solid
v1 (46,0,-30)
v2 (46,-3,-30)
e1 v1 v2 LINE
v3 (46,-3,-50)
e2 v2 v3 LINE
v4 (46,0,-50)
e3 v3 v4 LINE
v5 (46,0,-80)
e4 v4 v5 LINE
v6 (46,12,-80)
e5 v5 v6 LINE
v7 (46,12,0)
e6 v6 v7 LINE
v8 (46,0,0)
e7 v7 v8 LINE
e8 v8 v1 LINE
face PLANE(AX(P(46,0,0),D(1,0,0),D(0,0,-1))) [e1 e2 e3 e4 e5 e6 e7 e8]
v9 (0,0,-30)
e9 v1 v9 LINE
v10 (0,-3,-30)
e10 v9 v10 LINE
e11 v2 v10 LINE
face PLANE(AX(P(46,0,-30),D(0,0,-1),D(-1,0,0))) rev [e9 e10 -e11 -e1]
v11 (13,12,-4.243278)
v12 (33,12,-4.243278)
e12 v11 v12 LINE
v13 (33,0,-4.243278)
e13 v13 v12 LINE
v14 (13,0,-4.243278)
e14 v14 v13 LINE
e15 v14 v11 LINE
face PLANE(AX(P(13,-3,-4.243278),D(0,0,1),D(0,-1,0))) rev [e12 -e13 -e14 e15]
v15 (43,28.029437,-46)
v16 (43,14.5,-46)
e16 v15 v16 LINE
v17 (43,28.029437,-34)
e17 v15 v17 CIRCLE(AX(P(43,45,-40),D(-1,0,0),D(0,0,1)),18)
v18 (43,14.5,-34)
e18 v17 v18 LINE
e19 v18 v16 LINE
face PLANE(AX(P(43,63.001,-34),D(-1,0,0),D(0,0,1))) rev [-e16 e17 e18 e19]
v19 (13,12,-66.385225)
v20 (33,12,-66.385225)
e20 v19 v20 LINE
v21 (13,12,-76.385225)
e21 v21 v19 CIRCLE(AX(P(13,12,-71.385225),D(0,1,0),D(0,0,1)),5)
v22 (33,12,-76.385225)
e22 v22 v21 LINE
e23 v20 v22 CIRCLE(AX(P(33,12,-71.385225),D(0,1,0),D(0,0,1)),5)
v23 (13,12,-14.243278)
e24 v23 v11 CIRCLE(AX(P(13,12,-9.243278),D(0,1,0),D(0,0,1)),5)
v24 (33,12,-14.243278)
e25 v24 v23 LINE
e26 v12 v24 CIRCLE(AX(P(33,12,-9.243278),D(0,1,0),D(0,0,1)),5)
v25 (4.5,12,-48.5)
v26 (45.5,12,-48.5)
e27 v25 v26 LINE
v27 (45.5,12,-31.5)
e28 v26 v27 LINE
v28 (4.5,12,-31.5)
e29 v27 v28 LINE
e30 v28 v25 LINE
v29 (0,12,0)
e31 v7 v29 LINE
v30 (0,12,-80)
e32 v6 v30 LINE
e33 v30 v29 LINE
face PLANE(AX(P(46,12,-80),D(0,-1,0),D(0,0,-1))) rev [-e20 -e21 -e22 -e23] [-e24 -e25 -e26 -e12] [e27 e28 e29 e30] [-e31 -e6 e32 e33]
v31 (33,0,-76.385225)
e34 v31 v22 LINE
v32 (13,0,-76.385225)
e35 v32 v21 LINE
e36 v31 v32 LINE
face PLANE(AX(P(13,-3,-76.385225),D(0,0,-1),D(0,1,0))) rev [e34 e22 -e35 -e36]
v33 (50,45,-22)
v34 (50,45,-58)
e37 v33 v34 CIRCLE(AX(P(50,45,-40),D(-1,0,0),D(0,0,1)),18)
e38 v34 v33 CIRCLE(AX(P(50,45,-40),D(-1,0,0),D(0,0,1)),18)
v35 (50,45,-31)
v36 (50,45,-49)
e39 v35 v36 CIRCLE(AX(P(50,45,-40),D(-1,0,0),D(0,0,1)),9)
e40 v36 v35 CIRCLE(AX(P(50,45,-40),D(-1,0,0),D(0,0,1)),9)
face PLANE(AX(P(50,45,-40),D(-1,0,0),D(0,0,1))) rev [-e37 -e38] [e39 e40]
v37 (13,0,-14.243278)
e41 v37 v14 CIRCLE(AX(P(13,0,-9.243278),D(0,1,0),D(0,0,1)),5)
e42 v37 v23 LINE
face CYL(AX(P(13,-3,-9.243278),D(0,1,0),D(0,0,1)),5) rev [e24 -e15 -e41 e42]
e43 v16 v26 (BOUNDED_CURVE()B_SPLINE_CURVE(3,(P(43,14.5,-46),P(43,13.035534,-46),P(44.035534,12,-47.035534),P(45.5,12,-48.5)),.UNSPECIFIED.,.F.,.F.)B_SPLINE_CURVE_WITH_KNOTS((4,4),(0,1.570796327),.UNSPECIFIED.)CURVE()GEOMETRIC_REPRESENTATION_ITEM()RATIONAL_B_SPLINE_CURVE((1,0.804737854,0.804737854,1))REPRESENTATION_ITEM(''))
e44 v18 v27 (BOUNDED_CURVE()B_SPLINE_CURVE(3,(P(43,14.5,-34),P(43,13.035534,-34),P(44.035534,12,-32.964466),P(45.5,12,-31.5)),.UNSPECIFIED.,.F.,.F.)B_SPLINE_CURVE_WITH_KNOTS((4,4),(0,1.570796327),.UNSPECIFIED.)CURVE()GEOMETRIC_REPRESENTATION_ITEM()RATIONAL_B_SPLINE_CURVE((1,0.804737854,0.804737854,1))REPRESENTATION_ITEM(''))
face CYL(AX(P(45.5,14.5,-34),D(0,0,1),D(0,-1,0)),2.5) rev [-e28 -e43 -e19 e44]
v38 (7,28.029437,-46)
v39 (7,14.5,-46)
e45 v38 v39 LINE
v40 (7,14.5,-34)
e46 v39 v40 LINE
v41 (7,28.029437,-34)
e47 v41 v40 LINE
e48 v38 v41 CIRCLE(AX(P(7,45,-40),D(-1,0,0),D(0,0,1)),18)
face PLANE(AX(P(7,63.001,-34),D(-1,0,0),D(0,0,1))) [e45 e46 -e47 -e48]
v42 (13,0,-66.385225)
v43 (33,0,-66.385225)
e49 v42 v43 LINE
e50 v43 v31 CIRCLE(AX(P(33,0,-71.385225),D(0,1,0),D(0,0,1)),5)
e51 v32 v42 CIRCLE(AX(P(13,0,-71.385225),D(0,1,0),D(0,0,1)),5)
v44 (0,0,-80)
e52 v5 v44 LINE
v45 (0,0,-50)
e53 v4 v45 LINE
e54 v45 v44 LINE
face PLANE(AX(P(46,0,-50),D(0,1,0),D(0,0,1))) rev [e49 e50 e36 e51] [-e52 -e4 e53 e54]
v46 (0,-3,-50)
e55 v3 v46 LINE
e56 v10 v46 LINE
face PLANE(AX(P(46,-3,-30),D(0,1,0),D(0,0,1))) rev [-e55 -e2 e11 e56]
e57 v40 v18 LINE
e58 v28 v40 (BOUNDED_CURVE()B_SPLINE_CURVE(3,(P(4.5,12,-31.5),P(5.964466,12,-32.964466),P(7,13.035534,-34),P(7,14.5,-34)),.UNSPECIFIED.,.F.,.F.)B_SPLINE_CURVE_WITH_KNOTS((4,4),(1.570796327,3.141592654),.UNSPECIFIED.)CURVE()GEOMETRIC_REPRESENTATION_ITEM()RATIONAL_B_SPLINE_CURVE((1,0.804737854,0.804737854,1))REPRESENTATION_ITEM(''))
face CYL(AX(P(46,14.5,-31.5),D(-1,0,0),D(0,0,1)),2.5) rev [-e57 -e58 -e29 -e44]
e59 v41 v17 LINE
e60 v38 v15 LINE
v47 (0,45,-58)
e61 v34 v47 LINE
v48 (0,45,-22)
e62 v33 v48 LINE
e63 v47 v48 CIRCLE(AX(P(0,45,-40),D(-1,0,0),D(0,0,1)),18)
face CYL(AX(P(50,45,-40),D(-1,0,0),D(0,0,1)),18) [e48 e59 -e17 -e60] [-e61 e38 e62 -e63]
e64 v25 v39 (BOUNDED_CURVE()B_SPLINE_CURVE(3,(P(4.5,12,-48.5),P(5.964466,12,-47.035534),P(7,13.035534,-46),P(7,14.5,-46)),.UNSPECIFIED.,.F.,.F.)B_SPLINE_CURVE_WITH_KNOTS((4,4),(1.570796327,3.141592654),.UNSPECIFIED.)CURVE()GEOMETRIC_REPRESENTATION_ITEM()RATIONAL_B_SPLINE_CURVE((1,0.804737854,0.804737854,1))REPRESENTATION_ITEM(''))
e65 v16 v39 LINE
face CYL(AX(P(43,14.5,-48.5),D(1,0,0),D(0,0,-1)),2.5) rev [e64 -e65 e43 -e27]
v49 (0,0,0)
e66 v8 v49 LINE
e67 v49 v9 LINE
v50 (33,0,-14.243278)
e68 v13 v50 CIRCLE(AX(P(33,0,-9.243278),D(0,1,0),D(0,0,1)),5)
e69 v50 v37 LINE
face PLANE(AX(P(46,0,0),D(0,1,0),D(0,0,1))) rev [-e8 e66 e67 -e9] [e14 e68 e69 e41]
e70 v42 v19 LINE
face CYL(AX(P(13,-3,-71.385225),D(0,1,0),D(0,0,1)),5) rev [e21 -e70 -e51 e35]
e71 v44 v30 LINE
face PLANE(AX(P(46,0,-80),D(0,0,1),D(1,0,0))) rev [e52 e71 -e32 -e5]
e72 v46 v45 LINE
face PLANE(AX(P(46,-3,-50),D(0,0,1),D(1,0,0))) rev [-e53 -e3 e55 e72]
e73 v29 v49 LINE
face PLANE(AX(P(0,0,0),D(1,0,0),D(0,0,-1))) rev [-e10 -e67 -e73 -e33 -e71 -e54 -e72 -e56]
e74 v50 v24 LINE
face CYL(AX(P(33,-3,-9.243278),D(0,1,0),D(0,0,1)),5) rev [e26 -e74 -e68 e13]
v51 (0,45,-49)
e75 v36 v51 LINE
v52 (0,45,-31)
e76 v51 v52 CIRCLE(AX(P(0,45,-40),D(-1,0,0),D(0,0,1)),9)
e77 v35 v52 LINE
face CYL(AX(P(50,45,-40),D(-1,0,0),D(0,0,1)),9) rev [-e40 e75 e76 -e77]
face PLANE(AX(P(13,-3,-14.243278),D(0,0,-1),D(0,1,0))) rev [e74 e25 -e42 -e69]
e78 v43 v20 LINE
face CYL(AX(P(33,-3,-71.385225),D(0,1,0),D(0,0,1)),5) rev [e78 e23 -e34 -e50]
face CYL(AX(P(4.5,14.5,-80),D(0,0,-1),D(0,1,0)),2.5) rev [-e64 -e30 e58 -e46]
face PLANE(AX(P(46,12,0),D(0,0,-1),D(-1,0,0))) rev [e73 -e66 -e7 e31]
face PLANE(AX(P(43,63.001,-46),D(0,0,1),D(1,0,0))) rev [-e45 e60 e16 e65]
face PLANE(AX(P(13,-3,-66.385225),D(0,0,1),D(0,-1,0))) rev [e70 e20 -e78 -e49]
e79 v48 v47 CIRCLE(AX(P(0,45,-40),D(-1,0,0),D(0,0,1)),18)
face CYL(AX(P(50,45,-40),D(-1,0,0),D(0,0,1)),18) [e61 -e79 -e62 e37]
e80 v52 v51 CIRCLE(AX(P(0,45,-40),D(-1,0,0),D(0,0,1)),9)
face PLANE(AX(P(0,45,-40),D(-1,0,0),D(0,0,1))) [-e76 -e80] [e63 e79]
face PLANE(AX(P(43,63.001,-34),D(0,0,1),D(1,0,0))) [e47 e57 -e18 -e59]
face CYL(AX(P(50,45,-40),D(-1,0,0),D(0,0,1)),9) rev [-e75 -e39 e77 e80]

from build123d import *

# Parameters (mm, degrees)
BASE_PLATE_DEPTH             = 46
HUB_PROFILE_36_18_R          = 18
HUB_PROFILE_36_18_R_2        = 9
BEARING_HUB_36_BORE_18_DEPTH = 50
HUB_SUPPORT_WEB_REACH        = 109.243
HUB_SUPPORT_WEB_END_RADIUS   = 18
HUB_SUPPORT_PROFILE_W        = 36
HUB_SUPPORT_PROFILE_H        = 12
MOUNTING_SLOTS_2X_DEPTH      = 108.24271537
EDGE_FILLETS_R2_5_R          = 2.5


with BuildPart() as part:
    # Base Plate Profile → Base Plate (new body)
    with BuildSketch(Plane(origin=(0, 0, 0), x_dir=(0, 0, -1), z_dir=(1, 0, 0))):
        Polygon((0, 0), (30, 0), (30, -3), (50, -3), (50, 0), (80, 0), (80, 12), (0, 12), align=None)
    extrude(amount=BASE_PLATE_DEPTH)



with BuildPart() as body_2:
    # Hub Profile Ø36-Ø18 → Bearing Hub Ø36 Bore Ø18 (new body)
    with BuildSketch(Plane.ZY):
        with Locations((-40, 45)):
            Circle(HUB_PROFILE_36_18_R)
        with Locations((-40, 45)):
            Circle(HUB_PROFILE_36_18_R_2, mode=Mode.SUBTRACT)
    extrude(amount=-BEARING_HUB_36_BORE_18_DEPTH)


with BuildPart() as part_1:
    add(part.part)

    add(body_2.part)  # Hub Support Web merges body 2
    # Hub Support Web: up to this cylinder (the profile starts outside it)
    hub_support_web_end = Plane(origin=(25, 45, -40), z_dir=(-1, 0, 0)) * Cylinder(HUB_SUPPORT_WEB_END_RADIUS, 255.486, mode=Mode.PRIVATE)
    # Hub Support Profile → Hub Support Web (add, up to the surface)
    with BuildSketch(Plane(origin=(0, 12, 0), x_dir=(1, 0, 0), z_dir=(0, 1, 0)), mode=Mode.PRIVATE) as hub_support_web_sk1:
        with Locations((25, 40)):
            Rectangle(HUB_SUPPORT_PROFILE_W, HUB_SUPPORT_PROFILE_H)
    hub_support_web_tool1 = extrude(hub_support_web_sk1.sketch, amount=HUB_SUPPORT_WEB_REACH, mode=Mode.PRIVATE) - hub_support_web_end
    add(hub_support_web_tool1.solids().sort_by_distance((25, 12, -40))[0])

    # Mounting Slots Profile → Mounting Slots 2x (cut, through all)
    with BuildSketch(Plane(origin=(0, 12, 0), x_dir=(1, 0, 0), z_dir=(0, 1, 0))):
        with BuildLine():
            Line((13, 76.385225424), (33, 76.385225424))
            ThreePointArc((33, 76.385225424), (38, 71.385225424), (33, 66.385225424))
            Line((33, 66.385225424), (13, 66.385225424))
            ThreePointArc((13, 66.385225424), (8, 71.385225424), (13, 76.385225424))
        make_face()
        with BuildLine():
            Line((13, 14.243278019), (33, 14.243278019))
            ThreePointArc((33, 14.243278019), (38, 9.243278019), (33, 4.243278019))
            Line((33, 4.243278019), (13, 4.243278019))
            ThreePointArc((13, 4.243278019), (8, 9.243278019), (13, 14.243278019))
        make_face()
    extrude(amount=-MOUNTING_SLOTS_2X_DEPTH, mode=Mode.SUBTRACT)

    # Edge Fillets R2.5
    edge_fillets_r2_5_edges = [part_1.edges().sort_by_distance(p)[0] for p in [
        (25, 12, -34),
        (7, 12, -40),
        (25, 12, -46),
        (43, 12, -40),
    ]]
    fillet(edge_fillets_r2_5_edges, radius=EDGE_FILLETS_R2_5_R)


solid = part_1.part
